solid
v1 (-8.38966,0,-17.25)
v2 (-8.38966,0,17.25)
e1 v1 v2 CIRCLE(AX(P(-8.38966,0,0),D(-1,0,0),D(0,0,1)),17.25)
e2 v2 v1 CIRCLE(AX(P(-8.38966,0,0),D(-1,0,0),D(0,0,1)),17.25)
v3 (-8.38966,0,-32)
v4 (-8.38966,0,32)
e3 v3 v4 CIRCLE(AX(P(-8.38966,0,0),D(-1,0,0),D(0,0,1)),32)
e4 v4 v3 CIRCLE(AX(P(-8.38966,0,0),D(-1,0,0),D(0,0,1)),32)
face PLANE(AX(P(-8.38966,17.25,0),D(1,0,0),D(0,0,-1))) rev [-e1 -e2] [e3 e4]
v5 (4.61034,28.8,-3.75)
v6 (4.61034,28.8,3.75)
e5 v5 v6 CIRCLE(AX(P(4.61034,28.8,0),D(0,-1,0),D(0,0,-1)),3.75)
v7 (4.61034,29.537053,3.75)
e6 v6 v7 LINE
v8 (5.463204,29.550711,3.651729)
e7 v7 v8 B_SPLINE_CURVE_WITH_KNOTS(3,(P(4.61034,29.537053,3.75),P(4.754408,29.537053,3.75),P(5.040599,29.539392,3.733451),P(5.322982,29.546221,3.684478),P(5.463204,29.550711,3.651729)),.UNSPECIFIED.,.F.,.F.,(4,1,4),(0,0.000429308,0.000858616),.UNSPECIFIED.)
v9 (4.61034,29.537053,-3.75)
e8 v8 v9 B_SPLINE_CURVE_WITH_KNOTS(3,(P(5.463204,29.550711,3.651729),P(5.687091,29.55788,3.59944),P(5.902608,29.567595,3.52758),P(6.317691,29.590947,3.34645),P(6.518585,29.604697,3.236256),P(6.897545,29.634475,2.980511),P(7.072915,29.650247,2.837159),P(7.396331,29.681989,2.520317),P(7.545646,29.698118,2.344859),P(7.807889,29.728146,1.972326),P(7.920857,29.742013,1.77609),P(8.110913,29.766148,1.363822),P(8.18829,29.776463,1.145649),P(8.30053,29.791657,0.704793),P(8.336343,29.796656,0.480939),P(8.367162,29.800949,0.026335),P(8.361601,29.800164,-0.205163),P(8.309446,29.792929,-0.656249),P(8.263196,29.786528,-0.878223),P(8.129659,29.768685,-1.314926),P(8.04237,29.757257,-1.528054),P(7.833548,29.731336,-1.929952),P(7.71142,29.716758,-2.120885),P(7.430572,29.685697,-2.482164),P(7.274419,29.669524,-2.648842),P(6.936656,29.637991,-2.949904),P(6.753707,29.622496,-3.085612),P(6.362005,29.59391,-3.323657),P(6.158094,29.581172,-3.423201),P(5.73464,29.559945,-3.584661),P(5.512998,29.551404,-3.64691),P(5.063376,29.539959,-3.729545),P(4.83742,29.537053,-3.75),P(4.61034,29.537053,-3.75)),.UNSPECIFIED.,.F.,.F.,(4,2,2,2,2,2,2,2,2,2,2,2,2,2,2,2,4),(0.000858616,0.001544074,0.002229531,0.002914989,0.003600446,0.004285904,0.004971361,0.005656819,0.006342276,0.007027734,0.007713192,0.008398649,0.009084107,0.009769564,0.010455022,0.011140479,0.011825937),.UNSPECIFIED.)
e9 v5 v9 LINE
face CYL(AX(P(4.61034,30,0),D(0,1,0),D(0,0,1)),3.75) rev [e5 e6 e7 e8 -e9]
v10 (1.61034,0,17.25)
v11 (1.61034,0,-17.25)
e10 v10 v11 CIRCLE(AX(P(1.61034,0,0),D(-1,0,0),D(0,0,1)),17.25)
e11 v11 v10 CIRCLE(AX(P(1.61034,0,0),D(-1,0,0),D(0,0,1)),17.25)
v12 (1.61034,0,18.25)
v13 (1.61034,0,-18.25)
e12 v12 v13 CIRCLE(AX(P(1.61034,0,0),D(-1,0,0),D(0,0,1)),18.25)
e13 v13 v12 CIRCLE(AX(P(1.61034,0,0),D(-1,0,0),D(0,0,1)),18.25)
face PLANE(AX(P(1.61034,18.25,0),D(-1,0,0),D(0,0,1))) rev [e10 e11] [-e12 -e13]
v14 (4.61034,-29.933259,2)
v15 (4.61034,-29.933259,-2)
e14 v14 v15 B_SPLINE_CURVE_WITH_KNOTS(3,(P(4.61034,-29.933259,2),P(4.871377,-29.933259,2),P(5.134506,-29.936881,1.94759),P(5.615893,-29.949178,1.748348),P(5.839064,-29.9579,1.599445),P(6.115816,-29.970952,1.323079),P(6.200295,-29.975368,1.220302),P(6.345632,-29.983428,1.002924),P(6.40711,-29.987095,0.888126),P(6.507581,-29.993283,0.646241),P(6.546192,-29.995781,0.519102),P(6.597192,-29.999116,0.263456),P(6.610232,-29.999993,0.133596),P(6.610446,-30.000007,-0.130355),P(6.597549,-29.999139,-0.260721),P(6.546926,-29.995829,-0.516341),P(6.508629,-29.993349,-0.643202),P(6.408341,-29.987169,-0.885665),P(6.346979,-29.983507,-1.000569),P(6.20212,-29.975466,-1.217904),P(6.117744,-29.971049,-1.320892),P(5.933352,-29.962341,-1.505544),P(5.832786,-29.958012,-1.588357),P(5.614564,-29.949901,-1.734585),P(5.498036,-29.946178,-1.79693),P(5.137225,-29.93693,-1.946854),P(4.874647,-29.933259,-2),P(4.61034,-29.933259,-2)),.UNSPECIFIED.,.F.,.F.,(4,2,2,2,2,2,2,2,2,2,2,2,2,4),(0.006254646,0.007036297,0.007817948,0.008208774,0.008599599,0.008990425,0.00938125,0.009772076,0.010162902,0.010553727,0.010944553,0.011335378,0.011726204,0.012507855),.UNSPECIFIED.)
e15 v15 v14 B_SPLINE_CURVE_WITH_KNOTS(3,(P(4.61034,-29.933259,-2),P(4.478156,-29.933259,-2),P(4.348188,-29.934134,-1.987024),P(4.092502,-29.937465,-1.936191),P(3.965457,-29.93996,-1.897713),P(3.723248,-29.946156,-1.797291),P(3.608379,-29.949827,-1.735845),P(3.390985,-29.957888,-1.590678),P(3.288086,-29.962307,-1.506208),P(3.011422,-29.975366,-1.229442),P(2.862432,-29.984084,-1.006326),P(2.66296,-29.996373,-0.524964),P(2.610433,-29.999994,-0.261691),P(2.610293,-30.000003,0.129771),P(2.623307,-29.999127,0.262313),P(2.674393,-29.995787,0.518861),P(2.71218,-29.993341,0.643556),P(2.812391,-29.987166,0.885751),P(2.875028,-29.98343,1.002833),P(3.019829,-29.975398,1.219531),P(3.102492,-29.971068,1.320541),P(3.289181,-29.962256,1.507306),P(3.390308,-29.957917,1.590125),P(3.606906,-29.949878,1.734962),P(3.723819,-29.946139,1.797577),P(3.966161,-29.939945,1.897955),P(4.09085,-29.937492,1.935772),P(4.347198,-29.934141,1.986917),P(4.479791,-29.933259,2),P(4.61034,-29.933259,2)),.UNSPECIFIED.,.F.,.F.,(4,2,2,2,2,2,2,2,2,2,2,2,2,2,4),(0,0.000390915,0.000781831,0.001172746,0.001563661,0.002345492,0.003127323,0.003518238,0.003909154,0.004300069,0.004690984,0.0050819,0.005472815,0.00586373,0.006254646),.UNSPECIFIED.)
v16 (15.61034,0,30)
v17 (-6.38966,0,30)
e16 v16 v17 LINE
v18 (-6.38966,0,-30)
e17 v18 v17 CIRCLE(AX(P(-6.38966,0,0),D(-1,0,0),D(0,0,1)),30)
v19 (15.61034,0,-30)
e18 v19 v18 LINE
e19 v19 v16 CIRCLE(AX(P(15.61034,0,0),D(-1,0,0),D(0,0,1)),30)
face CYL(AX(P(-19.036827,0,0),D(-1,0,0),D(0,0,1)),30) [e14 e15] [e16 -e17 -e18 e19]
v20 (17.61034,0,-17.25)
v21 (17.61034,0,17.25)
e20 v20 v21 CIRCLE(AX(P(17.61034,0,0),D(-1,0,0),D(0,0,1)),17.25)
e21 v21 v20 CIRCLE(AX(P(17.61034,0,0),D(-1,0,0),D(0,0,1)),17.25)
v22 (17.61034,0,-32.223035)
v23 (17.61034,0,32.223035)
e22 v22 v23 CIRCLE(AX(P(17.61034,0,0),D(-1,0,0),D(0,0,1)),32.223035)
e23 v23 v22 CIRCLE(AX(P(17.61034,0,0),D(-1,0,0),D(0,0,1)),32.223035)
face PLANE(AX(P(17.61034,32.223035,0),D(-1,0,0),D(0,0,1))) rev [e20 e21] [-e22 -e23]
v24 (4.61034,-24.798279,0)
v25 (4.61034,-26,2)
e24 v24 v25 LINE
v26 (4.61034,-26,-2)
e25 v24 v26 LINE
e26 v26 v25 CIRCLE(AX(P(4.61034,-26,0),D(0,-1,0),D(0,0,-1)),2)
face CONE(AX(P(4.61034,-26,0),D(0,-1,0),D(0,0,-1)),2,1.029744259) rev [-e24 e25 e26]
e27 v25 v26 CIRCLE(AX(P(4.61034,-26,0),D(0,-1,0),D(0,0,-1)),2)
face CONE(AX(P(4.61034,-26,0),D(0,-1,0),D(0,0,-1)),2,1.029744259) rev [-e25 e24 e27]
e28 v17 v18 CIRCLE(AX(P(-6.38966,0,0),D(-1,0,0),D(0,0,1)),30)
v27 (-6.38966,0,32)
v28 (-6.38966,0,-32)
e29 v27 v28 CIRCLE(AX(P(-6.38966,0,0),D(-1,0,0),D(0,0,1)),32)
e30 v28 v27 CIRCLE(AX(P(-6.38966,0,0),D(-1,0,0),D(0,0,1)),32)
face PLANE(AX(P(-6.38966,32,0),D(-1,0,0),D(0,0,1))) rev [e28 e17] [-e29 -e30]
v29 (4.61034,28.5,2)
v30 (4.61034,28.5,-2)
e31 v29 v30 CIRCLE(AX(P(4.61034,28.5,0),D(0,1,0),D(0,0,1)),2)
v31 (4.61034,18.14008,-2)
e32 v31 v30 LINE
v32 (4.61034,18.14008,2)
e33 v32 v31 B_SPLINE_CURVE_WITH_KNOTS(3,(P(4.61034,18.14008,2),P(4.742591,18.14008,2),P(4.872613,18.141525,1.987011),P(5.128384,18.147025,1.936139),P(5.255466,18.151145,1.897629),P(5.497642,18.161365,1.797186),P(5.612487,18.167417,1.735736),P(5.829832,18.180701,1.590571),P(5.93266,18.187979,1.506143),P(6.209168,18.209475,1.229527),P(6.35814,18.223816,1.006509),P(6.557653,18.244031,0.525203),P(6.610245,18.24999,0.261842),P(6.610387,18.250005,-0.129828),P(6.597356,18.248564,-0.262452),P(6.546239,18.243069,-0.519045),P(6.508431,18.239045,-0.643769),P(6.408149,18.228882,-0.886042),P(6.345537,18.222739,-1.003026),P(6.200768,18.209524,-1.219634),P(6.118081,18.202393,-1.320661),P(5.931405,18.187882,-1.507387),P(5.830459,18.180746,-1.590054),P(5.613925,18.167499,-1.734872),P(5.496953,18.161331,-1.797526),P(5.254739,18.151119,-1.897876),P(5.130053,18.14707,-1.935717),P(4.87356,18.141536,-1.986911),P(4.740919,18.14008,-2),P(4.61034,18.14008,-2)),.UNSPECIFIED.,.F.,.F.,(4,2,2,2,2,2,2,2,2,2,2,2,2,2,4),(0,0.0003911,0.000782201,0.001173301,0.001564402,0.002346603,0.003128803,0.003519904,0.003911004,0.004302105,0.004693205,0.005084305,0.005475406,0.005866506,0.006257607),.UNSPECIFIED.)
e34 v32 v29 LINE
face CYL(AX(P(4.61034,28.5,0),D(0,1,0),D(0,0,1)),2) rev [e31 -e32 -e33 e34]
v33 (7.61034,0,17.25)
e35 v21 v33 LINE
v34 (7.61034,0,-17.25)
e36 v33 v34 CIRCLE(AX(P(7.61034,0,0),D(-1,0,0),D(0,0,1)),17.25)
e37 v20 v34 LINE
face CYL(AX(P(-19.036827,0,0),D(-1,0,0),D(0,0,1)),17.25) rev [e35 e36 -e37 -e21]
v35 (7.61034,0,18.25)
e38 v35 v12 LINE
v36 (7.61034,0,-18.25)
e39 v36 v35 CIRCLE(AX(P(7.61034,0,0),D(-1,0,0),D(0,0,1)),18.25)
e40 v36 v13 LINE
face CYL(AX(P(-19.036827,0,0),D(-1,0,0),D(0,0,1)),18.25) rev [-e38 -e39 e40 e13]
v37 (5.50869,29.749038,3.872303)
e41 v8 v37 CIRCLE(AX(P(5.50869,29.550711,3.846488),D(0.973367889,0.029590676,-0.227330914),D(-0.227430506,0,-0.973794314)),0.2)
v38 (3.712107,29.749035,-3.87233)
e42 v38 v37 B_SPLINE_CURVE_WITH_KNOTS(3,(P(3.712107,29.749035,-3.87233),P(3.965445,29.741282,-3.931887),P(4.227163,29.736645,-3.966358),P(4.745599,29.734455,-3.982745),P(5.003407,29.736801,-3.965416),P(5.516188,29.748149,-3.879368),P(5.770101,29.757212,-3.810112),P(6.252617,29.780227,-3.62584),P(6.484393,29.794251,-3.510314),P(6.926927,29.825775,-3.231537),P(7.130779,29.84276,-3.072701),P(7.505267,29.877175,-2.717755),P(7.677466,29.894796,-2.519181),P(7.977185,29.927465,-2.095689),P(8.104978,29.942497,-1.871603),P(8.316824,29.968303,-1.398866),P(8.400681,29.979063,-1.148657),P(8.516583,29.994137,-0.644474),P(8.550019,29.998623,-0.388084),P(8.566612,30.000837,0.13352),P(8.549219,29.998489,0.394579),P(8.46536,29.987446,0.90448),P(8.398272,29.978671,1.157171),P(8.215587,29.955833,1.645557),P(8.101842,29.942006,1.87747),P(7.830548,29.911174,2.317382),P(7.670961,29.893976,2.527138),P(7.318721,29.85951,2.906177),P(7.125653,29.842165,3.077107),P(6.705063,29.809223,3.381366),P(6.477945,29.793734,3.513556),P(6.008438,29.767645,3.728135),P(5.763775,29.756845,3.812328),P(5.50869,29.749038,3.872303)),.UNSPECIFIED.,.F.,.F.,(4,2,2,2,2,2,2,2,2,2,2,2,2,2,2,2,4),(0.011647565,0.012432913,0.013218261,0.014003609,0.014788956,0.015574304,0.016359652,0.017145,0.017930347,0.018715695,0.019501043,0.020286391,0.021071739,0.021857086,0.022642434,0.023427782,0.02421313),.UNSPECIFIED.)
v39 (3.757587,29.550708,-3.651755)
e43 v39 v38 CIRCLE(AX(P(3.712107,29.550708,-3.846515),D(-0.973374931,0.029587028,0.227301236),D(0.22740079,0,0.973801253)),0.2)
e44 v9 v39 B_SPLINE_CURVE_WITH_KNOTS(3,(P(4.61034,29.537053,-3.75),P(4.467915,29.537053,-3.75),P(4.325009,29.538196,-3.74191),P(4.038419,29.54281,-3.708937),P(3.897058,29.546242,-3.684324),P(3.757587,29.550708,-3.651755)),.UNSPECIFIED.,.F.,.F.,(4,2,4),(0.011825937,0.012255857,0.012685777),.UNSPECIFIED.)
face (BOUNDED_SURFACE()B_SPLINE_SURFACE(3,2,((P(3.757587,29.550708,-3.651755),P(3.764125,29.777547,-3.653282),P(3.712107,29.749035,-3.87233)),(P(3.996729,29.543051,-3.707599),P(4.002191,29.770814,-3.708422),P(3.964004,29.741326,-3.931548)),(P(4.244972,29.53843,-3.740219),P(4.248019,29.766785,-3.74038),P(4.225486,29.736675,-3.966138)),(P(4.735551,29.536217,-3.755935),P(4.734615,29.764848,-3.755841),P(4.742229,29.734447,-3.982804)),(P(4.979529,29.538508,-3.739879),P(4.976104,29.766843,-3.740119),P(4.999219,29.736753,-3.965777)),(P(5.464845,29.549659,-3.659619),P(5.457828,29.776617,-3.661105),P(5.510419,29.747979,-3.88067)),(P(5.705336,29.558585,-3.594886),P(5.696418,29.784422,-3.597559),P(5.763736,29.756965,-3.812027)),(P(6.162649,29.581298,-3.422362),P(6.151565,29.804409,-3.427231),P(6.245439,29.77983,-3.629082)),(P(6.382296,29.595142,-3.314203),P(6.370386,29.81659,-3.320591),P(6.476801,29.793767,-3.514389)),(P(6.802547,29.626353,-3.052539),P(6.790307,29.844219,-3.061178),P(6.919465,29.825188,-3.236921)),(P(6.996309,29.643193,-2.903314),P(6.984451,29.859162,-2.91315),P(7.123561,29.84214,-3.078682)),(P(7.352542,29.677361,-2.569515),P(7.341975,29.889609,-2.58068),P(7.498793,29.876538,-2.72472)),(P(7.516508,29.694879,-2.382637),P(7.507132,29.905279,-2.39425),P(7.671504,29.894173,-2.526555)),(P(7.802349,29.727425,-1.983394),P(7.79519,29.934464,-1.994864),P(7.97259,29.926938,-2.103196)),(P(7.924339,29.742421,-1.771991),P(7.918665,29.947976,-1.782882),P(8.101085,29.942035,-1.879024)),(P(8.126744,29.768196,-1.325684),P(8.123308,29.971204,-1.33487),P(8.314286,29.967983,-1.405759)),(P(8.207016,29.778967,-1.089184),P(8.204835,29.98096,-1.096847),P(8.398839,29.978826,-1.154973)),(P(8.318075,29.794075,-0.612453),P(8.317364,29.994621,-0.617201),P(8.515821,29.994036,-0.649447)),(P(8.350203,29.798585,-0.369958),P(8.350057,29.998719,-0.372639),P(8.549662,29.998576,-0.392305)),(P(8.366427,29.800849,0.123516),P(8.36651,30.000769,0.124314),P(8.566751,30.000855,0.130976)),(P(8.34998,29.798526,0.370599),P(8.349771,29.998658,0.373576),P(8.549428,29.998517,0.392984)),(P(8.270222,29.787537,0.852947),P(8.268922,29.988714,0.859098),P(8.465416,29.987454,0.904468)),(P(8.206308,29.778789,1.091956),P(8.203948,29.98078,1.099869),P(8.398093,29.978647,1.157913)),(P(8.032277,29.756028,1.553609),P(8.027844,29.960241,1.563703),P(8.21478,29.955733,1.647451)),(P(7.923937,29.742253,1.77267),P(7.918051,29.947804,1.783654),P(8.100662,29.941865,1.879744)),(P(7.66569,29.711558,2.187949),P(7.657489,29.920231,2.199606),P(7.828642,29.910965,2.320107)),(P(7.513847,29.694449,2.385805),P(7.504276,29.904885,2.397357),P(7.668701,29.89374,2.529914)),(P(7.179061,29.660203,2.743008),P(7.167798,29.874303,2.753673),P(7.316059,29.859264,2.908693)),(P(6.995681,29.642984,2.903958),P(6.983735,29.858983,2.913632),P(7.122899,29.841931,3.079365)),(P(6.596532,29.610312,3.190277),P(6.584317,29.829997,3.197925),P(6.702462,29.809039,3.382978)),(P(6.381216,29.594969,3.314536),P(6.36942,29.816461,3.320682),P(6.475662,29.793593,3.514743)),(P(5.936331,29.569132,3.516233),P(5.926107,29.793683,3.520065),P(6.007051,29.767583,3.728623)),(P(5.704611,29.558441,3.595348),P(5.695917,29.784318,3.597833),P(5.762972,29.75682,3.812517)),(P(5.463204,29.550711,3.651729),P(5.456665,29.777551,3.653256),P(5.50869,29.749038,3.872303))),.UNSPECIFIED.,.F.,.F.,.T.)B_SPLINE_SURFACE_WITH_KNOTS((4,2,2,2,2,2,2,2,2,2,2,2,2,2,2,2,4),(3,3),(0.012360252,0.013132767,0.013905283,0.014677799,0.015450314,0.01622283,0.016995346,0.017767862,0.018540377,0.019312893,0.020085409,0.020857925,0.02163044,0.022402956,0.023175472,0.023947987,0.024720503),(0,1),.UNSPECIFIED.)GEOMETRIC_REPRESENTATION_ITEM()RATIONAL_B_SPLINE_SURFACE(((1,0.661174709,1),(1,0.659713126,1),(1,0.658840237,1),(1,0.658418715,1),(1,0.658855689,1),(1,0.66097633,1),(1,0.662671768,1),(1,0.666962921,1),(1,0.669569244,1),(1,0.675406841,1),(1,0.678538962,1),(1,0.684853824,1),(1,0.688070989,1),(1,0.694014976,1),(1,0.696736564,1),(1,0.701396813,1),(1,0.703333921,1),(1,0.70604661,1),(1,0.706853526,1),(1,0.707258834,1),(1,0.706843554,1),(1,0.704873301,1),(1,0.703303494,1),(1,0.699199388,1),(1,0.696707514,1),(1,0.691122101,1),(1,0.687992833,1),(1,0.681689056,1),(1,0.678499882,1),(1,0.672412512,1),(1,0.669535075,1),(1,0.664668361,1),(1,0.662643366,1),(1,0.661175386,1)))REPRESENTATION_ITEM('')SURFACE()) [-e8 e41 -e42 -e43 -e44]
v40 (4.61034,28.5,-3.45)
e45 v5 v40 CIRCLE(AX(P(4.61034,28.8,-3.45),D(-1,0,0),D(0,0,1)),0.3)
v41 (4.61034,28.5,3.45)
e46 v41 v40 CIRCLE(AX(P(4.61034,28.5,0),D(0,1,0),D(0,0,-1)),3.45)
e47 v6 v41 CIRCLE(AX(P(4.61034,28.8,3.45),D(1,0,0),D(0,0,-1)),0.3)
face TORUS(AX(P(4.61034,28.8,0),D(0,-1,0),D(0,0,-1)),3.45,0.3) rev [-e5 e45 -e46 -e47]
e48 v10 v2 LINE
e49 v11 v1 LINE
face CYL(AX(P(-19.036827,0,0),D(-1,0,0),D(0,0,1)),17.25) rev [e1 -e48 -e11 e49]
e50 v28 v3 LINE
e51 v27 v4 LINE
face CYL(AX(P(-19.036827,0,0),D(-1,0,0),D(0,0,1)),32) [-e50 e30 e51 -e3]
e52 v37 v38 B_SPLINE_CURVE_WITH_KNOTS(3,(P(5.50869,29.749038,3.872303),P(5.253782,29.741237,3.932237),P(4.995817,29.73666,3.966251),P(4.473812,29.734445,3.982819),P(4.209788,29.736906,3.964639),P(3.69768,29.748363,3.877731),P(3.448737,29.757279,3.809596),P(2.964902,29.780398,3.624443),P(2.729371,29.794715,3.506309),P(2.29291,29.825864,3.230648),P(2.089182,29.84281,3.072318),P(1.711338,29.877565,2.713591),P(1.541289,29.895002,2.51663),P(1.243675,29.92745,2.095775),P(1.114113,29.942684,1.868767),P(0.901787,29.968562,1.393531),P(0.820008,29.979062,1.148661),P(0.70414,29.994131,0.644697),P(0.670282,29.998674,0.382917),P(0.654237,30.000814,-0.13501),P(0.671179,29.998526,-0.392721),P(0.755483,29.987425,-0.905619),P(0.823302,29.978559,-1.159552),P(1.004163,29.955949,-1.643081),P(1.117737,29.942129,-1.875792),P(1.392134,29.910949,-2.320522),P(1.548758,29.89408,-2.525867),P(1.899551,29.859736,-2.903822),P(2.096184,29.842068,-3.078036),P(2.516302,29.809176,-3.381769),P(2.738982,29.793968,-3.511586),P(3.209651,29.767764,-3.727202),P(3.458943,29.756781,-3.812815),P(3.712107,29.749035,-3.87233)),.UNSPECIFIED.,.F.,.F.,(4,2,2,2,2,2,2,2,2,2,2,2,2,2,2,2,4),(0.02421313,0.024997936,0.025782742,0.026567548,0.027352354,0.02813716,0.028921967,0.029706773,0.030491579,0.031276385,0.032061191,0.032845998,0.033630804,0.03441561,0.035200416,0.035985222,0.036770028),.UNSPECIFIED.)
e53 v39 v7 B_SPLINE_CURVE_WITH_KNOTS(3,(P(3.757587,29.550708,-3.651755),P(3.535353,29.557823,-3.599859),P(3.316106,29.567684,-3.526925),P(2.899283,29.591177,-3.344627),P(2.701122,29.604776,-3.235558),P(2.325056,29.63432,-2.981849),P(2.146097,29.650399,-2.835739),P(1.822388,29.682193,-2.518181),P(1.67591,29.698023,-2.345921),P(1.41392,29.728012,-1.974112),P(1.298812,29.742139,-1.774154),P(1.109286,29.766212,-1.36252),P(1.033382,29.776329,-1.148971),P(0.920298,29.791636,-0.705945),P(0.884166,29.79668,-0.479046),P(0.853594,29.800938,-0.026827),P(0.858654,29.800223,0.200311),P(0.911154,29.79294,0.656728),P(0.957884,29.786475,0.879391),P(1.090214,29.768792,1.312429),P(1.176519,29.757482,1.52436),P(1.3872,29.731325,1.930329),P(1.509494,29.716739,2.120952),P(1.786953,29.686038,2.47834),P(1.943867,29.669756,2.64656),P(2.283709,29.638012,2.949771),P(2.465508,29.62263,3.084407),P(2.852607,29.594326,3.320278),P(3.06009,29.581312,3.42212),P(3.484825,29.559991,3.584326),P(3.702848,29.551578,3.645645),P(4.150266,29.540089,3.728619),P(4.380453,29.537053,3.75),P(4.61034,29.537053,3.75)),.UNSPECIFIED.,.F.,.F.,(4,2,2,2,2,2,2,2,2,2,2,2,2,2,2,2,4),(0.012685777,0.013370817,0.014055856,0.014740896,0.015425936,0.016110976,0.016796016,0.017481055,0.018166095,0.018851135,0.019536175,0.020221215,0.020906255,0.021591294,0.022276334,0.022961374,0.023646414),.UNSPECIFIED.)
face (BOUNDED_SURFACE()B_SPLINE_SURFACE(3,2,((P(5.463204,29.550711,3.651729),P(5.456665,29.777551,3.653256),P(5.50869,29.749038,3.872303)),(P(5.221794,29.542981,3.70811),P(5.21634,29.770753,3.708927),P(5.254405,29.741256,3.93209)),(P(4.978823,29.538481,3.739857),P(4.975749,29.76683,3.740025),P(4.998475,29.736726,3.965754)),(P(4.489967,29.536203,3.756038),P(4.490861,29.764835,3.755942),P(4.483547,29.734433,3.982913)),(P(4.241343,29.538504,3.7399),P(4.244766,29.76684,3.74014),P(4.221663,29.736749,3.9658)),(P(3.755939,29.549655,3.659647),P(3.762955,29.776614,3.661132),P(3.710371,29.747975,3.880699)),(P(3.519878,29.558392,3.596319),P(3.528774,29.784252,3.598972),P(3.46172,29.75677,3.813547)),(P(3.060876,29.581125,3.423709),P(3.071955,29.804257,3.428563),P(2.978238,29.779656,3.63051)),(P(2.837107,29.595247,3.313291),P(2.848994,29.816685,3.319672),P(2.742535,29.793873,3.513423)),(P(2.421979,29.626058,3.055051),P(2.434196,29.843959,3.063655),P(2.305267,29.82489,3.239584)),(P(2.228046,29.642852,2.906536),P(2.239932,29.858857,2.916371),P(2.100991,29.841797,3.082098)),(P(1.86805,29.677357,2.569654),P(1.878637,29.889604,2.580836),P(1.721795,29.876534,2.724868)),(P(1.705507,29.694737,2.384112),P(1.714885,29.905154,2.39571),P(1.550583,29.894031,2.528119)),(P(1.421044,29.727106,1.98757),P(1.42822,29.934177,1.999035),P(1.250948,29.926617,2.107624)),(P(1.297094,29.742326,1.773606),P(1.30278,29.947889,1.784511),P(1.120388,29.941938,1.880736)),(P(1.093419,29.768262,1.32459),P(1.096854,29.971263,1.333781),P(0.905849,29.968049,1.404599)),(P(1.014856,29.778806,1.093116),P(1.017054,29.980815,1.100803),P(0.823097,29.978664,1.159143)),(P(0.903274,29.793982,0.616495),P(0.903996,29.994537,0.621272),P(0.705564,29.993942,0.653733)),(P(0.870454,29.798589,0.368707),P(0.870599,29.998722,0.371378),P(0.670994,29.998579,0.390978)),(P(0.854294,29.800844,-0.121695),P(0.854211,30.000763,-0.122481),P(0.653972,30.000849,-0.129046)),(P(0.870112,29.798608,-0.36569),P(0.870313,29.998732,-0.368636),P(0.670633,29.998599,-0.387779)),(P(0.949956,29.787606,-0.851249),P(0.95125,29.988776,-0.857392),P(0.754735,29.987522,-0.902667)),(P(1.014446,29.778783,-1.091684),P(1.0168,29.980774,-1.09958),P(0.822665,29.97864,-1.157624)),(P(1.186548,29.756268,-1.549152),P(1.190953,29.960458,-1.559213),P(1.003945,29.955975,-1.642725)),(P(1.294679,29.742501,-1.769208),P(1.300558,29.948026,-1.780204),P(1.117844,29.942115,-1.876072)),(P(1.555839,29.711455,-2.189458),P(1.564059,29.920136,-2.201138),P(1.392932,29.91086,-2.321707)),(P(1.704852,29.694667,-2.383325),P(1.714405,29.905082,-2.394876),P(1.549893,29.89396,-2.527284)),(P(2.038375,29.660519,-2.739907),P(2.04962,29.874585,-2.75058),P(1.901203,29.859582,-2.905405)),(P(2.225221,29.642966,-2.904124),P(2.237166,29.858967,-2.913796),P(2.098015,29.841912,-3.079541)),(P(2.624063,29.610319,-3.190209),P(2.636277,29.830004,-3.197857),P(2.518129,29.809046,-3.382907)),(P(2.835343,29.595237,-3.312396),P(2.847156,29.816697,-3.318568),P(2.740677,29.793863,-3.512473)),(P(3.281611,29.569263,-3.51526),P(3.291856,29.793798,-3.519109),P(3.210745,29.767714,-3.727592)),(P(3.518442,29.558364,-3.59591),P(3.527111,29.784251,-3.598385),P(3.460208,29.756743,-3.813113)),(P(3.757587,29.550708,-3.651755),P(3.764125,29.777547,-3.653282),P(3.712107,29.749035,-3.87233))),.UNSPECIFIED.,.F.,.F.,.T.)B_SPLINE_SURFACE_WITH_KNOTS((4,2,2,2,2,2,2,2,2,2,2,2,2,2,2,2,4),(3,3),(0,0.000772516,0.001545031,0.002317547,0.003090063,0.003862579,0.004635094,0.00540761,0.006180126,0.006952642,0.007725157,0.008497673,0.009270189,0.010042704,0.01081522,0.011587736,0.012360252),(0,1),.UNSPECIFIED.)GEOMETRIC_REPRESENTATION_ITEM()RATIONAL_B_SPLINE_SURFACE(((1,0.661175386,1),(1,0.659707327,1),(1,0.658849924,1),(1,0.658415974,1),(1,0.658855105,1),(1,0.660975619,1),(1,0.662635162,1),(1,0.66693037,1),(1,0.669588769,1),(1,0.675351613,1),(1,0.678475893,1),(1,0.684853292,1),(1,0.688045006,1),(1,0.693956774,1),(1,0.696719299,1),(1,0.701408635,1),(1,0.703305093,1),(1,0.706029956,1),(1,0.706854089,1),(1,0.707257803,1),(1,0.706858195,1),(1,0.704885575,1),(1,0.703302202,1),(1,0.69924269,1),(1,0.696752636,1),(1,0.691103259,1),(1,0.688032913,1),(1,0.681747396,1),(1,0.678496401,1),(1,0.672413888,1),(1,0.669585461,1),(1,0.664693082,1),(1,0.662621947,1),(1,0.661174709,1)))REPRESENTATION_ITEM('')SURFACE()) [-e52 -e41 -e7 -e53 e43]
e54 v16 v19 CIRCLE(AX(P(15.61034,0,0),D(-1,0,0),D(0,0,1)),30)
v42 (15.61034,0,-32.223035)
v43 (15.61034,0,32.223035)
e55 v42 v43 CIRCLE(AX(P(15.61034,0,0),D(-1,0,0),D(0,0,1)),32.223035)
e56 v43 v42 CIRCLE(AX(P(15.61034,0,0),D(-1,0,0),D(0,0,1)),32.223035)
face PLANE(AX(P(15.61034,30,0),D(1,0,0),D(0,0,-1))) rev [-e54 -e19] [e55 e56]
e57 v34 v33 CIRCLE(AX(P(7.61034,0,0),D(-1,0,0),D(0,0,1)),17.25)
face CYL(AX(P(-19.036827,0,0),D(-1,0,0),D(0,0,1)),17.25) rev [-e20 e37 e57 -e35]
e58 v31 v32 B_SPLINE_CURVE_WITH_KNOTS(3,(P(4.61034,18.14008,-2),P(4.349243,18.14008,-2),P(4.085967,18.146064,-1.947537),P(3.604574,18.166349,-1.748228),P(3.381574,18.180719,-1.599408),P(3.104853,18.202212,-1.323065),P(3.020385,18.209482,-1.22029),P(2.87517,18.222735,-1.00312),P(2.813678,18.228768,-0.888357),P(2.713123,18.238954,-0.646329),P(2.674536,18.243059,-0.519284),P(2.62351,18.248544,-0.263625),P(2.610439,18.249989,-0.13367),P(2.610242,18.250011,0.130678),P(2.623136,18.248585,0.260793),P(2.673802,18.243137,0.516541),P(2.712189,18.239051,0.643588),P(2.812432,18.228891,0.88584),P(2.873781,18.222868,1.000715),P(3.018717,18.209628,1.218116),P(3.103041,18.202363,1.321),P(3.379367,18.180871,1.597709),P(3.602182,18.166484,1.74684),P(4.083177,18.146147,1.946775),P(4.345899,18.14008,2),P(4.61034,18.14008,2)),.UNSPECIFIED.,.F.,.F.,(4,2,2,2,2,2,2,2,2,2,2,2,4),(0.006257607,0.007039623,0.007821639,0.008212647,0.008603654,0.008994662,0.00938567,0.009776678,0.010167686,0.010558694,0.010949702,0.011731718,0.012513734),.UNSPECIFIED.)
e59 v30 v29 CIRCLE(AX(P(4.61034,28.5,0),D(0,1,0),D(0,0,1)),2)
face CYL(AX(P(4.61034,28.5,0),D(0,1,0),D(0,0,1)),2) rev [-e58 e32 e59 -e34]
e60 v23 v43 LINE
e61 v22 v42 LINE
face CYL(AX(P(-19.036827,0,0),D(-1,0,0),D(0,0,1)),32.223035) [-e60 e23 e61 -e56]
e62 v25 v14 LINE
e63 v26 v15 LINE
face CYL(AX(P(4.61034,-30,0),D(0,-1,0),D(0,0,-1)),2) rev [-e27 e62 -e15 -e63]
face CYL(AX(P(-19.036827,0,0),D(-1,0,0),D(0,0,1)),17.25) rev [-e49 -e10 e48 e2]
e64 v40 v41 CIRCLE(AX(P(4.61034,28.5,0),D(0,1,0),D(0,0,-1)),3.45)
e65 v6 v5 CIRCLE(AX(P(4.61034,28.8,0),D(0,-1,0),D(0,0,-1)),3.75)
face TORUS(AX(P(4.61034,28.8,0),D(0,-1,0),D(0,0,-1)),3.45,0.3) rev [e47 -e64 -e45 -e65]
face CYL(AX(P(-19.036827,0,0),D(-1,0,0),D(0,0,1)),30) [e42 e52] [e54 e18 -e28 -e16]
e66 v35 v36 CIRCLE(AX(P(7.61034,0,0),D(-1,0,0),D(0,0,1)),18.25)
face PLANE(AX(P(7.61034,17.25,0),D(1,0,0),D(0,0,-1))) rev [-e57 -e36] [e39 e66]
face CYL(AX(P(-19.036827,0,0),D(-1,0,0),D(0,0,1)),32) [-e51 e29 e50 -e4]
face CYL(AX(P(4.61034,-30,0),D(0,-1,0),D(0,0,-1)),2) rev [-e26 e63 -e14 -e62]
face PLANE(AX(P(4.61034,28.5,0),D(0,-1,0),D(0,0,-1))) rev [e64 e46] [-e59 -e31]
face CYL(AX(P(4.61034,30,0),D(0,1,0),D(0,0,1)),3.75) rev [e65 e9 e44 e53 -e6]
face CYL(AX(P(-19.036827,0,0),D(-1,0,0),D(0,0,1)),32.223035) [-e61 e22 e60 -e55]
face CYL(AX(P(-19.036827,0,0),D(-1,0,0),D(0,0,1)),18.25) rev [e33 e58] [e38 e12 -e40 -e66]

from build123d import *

# Parameters (mm, degrees)
HOLE1_D           = 7.5
HOLE1_DEPTH       = 1.5
HOLE2_REACH       = 72.963
HOLE2_BORE_R      = 2
DOWEL_HOLE1_D     = 4
DOWEL_HOLE1_DEPTH = 4
DOWEL_HOLE1_TIP   = 1.201721238
FILLET1_R         = 0.2
FILLET2_R         = 0.3


with BuildPart() as part:
    # Sketch1 → Revolve1 (revolve)
    with BuildSketch(Plane.XY, mode=Mode.PRIVATE) as revolve1_sk:
        Polygon((-8.389660143, 17.25), (-8.389660143, 32), (-6.389660143, 32), (-6.389660143, 30), (15.610339857, 30), (15.610339857, 32.223034735), (17.610339857, 32.223034735), (17.610339857, 17.25), (7.610339857, 17.25), (7.610339857, 18.25), (1.610339857, 18.25), (1.610339857, 17.25), align=None)
    revolve(revolve1_sk.sketch.rotate(Axis((-19.036826505, 0, 0), (1, 0, 0)), 90), axis=Axis((-19.036826505, 0, 0), (1, 0, 0)))

    # Hole1
    with Locations(Plane(origin=(0, 30, 0), x_dir=(1, 0, 0), z_dir=(0, 1, 0))):
        with Locations((4.610339857, 0)):
            Hole(HOLE1_D / 2, depth=HOLE1_DEPTH)

    # Hole2 bore → Hole2 (cut, up to next)
    with BuildSketch(Plane(origin=(0, 28.5, 0), x_dir=(1, 0, 0), z_dir=(0, 1, 0)), mode=Mode.PRIVATE) as hole2_sk1:
        with Locations((4.610339857, 0)):
            Circle(HOLE2_BORE_R)
    hole2_tool1 = extrude(hole2_sk1.sketch, amount=-HOLE2_REACH, mode=Mode.PRIVATE) & part.part
    add(hole2_tool1.solids().sort_by_distance((4.61034, 28.5, 0))[0], mode=Mode.SUBTRACT)

    # Dowel Hole1
    with Locations(Plane(origin=(0, -30, 0), x_dir=(-1, 0, 0), z_dir=(0, -1, 0))):
        with Locations((-4.610339857, 0)):
            Hole(DOWEL_HOLE1_D / 2, depth=DOWEL_HOLE1_DEPTH)
            with Locations((0, 0, -(DOWEL_HOLE1_DEPTH + DOWEL_HOLE1_TIP / 2))):  # 118° drill point
                Cone(0, DOWEL_HOLE1_D / 2, DOWEL_HOLE1_TIP, mode=Mode.SUBTRACT)

    # Fillet1
    fillet1_edges = [part.edges().sort_by_distance(p)[0] for p in [
        (8.360339864, 29.999999997, -1e-09),
    ]]
    fillet(fillet1_edges, radius=FILLET1_R)

    # Fillet2
    fillet2_edges = [part.edges().sort_by_distance(p)[0] for p in [
        (8.360339857, 28.5, 0),
    ]]
    fillet(fillet2_edges, radius=FILLET2_R)


solid = part.part
